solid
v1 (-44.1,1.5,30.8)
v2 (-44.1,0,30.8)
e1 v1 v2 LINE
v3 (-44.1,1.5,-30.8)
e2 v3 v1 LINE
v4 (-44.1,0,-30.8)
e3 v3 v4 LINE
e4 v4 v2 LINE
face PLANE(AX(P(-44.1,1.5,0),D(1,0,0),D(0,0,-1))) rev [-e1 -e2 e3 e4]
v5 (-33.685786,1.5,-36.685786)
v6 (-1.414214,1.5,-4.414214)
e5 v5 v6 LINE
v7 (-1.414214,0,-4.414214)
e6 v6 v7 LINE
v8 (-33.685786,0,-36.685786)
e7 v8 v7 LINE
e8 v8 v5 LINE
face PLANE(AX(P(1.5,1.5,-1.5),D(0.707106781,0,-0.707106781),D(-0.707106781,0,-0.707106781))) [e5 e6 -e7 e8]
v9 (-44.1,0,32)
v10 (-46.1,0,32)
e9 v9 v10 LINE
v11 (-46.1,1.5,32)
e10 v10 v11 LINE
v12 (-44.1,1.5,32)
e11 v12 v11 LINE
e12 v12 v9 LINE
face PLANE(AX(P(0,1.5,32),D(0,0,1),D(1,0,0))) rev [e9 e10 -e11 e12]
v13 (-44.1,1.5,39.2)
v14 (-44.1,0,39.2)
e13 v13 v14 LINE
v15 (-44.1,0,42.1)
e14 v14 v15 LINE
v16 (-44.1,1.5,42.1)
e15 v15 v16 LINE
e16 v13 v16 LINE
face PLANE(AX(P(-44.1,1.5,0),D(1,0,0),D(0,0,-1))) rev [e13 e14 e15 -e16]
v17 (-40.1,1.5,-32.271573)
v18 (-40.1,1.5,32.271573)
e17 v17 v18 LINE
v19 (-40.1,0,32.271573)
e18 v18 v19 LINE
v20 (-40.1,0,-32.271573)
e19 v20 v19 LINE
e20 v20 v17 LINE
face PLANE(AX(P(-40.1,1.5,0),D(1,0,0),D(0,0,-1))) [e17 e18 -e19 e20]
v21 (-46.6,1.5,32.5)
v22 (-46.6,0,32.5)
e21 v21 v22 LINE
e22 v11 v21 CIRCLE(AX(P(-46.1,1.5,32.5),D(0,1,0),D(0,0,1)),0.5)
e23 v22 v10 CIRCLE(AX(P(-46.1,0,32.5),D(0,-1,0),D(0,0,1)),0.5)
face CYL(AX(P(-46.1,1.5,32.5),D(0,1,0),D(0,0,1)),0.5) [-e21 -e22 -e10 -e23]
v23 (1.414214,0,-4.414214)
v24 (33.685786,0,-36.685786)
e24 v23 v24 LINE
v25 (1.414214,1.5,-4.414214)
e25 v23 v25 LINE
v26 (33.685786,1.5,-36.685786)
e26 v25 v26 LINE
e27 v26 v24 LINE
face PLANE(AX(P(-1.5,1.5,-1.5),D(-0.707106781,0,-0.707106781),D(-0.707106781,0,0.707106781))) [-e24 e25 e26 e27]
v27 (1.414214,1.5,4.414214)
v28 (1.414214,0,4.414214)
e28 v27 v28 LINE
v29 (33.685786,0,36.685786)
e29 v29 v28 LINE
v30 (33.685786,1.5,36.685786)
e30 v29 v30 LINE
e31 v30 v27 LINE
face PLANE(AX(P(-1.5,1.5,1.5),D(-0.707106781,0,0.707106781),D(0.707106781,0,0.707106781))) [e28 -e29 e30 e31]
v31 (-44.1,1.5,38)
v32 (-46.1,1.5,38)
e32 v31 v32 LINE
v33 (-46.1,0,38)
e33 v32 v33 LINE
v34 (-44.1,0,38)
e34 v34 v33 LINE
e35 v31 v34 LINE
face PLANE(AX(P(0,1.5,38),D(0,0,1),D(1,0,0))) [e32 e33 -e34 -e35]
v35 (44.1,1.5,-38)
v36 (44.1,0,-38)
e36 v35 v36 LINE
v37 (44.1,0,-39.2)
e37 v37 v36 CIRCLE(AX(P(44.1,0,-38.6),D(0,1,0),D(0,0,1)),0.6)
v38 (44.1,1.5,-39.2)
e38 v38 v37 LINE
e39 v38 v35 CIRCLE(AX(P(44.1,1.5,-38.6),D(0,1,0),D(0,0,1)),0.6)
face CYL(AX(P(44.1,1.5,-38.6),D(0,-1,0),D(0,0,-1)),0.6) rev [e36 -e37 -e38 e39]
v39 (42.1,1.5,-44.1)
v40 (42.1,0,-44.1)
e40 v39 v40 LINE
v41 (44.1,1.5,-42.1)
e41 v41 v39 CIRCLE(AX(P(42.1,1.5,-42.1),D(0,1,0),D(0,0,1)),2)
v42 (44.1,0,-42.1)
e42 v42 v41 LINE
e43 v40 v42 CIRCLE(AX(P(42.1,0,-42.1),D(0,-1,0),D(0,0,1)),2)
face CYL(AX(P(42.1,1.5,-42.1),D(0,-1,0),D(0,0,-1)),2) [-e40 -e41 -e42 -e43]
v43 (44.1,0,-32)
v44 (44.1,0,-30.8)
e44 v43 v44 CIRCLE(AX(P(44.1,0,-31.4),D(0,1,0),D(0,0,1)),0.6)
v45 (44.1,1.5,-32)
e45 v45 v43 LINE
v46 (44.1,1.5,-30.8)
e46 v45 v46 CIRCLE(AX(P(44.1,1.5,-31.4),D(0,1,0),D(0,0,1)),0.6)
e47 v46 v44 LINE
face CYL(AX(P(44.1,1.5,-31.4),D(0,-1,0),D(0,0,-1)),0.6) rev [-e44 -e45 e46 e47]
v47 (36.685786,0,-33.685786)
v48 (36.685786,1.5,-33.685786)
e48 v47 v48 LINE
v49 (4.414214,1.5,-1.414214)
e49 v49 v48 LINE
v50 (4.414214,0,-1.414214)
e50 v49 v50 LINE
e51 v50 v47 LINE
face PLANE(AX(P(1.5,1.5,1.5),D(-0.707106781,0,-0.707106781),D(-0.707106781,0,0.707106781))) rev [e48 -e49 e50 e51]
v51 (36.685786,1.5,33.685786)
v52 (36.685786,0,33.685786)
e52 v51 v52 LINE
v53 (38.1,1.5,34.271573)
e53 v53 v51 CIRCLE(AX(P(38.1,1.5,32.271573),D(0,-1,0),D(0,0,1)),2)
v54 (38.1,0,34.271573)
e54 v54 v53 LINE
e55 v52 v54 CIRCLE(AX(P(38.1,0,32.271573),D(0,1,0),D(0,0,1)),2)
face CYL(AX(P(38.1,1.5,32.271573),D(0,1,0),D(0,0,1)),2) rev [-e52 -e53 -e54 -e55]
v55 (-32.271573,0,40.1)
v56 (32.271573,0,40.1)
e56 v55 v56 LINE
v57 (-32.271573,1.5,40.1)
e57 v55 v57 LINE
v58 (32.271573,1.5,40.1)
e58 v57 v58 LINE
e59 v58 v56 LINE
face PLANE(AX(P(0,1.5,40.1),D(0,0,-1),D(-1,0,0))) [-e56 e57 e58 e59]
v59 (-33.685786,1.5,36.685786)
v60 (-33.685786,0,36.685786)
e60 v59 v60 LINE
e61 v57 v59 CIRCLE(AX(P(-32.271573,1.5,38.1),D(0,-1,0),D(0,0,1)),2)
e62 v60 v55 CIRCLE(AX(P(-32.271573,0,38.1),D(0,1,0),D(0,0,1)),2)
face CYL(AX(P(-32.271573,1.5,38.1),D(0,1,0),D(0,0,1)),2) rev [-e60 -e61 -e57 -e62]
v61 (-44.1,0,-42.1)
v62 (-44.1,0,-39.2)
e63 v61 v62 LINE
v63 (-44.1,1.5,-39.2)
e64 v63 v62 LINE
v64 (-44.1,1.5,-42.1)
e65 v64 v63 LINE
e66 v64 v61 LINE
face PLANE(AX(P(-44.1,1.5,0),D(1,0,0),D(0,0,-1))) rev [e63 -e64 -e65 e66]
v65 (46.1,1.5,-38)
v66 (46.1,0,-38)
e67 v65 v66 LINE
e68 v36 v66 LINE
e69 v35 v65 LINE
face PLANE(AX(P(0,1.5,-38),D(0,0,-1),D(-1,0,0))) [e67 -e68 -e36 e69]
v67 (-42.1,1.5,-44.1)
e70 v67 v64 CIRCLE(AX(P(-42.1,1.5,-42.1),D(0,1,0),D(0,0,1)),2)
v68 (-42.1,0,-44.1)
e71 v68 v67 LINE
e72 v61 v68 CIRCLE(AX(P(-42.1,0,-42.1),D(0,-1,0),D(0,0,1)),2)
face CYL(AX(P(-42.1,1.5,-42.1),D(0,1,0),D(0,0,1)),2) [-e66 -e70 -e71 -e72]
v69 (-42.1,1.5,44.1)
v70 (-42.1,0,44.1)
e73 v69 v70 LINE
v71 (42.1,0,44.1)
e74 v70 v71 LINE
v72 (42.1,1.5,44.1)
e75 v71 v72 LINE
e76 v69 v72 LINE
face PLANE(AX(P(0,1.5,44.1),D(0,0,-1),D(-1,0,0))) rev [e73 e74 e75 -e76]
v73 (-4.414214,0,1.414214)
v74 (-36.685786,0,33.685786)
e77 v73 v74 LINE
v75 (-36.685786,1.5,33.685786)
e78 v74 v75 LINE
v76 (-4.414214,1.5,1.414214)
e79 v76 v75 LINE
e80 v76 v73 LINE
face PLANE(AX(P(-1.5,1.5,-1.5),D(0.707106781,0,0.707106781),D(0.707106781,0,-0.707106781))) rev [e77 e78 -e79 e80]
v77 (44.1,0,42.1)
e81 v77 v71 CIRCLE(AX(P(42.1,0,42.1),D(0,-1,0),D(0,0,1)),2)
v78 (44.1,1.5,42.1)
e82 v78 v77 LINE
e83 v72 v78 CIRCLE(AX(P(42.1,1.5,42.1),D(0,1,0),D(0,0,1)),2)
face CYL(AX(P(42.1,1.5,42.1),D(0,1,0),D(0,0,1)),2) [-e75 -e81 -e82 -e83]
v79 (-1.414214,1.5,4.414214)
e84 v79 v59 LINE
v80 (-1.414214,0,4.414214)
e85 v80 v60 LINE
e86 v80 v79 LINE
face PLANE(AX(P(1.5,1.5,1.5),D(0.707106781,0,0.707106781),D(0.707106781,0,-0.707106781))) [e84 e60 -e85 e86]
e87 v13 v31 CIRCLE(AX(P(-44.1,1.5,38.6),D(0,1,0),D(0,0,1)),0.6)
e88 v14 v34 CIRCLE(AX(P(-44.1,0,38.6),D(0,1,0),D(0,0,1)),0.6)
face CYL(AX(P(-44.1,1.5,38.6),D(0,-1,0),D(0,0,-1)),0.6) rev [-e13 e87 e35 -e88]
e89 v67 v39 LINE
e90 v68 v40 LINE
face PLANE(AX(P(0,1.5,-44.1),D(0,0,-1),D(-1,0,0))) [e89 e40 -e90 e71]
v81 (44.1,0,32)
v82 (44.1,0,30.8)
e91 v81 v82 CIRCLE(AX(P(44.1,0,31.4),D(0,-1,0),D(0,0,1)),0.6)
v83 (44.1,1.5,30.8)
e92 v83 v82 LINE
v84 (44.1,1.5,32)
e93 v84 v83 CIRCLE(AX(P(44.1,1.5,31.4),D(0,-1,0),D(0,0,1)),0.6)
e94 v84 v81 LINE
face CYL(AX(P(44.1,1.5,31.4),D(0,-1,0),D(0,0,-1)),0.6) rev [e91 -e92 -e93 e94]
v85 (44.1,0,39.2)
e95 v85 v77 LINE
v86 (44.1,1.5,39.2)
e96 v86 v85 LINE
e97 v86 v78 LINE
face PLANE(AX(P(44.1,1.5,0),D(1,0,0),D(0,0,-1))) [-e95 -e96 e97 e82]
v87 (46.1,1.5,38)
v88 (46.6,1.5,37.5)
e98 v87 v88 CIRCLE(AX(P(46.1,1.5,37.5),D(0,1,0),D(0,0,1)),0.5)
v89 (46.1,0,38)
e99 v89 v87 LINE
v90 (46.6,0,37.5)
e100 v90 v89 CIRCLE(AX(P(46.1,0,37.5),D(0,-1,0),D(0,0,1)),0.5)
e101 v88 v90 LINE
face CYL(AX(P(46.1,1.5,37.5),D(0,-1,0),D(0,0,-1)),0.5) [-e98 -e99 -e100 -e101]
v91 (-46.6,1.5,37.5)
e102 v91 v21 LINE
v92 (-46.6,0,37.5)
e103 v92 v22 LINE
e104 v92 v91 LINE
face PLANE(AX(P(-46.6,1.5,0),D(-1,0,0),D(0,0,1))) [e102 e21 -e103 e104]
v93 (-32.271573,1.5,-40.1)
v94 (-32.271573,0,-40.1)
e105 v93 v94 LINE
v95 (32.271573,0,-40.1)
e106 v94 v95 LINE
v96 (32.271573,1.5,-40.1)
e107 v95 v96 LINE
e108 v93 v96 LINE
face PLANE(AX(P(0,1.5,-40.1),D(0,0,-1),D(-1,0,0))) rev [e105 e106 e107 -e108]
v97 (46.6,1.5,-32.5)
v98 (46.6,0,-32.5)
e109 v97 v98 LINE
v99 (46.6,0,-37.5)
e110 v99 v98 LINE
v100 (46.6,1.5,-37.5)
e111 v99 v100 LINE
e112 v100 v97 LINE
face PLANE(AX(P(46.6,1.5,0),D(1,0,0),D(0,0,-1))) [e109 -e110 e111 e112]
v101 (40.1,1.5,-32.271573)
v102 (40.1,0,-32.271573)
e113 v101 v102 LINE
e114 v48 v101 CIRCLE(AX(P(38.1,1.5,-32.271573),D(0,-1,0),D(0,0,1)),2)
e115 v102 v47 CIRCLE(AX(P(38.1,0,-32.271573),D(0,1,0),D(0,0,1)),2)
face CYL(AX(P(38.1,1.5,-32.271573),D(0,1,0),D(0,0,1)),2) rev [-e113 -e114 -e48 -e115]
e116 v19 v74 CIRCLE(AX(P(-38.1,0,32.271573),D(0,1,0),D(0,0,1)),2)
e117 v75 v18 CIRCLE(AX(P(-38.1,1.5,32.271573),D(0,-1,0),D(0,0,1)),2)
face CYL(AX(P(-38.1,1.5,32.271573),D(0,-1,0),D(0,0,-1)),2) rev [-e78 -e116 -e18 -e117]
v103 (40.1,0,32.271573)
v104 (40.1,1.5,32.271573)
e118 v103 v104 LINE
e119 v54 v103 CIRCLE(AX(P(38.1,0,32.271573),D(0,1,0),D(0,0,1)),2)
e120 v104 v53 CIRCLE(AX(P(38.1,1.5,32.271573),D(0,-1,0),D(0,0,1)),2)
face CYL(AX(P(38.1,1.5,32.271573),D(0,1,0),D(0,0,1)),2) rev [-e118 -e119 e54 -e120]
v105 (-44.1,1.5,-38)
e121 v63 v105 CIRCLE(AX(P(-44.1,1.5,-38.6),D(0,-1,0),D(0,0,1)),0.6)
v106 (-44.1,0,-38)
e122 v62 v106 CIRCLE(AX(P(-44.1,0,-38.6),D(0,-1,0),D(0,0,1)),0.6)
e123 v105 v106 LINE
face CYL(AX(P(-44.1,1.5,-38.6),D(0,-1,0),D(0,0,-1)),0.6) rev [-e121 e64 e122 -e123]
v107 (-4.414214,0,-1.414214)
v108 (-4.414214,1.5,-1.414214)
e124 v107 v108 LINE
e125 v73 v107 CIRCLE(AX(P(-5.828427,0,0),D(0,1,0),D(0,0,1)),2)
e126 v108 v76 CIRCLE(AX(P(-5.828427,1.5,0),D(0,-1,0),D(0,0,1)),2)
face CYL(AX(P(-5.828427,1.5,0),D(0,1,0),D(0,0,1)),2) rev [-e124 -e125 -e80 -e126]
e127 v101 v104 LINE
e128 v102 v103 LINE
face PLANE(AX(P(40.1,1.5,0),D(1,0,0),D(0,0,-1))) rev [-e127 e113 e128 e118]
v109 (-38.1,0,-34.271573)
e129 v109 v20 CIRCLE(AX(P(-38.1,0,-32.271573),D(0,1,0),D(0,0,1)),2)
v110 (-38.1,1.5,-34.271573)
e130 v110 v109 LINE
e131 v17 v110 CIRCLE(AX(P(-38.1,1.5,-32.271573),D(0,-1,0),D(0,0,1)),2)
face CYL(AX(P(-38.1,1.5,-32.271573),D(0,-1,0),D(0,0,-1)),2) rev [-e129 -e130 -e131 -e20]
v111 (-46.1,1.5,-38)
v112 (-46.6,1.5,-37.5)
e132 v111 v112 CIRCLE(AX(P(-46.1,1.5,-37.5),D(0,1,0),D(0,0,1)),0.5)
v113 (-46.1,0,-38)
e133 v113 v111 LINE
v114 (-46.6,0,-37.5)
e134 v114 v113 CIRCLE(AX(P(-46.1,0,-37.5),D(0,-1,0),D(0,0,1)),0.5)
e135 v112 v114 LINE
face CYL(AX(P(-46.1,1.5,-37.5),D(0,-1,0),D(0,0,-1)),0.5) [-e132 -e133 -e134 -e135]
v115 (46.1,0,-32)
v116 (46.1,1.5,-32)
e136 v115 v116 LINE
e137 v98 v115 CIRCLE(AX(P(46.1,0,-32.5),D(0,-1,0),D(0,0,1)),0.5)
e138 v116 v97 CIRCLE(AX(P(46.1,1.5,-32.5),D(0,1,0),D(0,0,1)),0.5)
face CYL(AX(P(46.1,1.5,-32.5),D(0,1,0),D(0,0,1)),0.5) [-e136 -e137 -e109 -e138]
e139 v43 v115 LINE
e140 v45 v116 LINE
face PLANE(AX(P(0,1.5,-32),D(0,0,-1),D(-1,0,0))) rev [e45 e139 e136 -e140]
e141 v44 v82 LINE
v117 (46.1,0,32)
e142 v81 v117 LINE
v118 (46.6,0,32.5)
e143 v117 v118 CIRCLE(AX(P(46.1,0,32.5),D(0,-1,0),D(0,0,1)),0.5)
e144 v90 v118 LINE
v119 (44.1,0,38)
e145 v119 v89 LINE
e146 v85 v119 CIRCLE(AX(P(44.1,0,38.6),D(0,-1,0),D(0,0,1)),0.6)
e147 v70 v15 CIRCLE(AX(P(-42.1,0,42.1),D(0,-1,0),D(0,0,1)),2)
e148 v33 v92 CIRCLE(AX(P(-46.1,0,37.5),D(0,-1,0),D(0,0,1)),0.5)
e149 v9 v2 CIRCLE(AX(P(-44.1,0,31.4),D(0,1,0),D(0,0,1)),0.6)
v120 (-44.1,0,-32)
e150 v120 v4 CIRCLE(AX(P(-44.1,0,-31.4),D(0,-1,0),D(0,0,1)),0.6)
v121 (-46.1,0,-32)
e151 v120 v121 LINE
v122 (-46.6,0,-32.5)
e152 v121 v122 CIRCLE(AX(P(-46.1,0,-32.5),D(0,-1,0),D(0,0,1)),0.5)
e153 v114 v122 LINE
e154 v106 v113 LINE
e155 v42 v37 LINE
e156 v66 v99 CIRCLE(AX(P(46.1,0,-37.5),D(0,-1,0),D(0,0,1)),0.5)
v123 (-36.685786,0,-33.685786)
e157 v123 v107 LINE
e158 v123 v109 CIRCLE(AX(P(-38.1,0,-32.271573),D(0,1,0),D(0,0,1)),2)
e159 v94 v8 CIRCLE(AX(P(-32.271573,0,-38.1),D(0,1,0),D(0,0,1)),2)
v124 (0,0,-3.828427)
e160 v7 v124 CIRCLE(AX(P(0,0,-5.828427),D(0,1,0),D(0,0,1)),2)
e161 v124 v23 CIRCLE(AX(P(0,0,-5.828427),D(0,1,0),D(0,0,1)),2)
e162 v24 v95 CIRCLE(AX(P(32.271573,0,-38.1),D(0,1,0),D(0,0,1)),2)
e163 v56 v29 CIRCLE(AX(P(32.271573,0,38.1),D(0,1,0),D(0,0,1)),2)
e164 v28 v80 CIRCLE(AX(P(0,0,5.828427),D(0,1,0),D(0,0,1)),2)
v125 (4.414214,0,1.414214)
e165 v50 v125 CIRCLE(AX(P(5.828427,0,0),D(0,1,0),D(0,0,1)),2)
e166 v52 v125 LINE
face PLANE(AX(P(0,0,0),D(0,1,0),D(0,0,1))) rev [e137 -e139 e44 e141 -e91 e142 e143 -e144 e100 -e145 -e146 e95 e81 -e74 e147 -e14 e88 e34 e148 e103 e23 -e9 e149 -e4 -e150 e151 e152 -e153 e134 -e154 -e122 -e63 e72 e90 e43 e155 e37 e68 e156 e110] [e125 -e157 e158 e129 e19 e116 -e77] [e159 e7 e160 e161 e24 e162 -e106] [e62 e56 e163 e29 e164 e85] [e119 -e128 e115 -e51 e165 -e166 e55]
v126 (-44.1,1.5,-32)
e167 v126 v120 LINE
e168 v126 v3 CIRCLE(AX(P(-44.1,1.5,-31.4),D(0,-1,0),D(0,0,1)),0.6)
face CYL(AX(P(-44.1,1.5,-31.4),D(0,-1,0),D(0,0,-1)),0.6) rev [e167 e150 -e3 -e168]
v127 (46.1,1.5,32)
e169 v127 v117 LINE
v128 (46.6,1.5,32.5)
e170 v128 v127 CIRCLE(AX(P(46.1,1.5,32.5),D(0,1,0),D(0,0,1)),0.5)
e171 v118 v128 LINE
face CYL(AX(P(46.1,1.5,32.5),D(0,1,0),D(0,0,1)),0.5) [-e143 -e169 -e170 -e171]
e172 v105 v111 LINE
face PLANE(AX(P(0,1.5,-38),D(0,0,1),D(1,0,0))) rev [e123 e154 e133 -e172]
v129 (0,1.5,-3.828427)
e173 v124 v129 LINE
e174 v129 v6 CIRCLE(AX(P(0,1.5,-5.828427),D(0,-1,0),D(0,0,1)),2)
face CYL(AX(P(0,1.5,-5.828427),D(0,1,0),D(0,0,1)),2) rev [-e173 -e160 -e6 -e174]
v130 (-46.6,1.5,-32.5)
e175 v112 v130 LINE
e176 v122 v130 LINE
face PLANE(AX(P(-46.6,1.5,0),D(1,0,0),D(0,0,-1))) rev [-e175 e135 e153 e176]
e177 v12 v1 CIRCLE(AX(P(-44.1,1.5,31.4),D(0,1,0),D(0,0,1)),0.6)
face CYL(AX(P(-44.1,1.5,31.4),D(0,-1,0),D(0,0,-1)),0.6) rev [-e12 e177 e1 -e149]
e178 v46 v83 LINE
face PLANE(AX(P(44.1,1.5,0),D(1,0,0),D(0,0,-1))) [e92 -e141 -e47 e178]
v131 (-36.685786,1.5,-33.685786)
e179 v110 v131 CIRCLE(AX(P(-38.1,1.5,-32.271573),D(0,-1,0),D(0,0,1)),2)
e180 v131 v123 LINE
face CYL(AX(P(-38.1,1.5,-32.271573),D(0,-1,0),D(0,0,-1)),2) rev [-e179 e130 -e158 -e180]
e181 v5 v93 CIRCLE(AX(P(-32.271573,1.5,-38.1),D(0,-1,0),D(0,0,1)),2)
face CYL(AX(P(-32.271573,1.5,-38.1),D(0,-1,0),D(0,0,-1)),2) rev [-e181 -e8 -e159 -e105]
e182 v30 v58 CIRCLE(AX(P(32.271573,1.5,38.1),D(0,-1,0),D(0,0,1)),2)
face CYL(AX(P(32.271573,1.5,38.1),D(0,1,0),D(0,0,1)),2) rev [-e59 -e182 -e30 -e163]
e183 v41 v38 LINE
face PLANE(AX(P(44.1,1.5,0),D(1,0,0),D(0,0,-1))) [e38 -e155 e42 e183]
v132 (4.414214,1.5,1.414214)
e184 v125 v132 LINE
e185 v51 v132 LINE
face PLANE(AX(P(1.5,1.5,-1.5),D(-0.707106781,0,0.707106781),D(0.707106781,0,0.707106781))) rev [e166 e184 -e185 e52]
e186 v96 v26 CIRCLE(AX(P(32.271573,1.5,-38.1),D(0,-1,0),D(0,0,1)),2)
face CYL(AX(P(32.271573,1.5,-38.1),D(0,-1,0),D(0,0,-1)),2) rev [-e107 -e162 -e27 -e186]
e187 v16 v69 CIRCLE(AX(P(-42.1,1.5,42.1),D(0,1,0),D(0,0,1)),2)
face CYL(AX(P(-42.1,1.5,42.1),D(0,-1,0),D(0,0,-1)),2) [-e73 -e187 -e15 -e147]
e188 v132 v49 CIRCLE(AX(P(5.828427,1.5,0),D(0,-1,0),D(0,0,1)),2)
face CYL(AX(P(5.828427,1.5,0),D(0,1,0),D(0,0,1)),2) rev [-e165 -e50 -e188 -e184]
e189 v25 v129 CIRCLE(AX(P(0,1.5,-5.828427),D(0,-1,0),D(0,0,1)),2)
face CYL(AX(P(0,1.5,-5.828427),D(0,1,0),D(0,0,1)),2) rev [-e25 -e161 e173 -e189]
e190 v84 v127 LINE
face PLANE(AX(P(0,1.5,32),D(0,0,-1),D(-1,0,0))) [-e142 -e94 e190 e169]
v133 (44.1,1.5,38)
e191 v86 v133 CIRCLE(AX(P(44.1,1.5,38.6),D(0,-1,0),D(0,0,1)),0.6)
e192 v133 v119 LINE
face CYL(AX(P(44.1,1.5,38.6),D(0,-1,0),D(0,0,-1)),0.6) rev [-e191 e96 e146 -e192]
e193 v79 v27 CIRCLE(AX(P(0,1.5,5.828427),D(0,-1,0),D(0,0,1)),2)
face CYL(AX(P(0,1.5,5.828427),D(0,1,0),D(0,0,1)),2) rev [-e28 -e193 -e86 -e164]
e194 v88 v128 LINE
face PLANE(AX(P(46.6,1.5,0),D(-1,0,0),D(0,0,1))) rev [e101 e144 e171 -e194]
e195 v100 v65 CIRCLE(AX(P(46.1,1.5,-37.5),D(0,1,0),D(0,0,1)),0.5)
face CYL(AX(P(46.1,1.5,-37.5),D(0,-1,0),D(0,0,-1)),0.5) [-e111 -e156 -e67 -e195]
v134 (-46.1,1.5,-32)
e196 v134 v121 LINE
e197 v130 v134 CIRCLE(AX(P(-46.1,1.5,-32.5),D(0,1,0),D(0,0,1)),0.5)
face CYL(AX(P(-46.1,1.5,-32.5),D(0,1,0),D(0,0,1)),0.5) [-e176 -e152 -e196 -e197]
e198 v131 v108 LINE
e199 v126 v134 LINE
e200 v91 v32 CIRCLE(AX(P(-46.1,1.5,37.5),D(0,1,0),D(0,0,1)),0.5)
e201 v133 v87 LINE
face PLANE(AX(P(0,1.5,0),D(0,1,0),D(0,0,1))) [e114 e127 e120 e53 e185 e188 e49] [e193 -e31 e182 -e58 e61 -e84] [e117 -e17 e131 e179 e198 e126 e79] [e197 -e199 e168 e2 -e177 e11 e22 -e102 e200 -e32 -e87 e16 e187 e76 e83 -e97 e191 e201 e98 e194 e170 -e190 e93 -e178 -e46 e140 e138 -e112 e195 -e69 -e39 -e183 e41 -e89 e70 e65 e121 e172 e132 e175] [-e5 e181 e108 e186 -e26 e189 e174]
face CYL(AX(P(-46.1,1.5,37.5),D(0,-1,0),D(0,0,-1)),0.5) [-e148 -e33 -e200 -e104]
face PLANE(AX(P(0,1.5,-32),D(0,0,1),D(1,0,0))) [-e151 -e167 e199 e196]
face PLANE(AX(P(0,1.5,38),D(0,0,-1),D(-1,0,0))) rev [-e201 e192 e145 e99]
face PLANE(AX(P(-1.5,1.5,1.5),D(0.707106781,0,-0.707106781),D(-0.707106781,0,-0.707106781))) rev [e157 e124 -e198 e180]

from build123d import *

# Parameters (mm, degrees)
EXTRUDE_1_DEPTH = 1.5
FILLET_1_R      = 0.5
FILLET_2_R      = 2


with BuildPart() as part:
    # 草图1 → 凸台-拉伸1 (new body)
    with BuildSketch(Plane(origin=(0, 0, 0), x_dir=(1, 0, 0), z_dir=(0, 1, 0))):
        with BuildLine():
            Line((44.1, 44.1), (-44.1, 44.1))
            Line((-44.1, 44.1), (-44.1, 39.2))
            ThreePointArc((-44.1, 39.2), (-43.5, 38.6), (-44.1, 38))
            Line((-44.1, 38), (-46.6, 38))
            Line((-46.6, 38), (-46.6, 32))
            Line((-46.6, 32), (-44.1, 32))
            ThreePointArc((-44.1, 32), (-43.5, 31.4), (-44.1, 30.8))
            Line((-44.1, 30.8), (-44.1, -30.8))
            ThreePointArc((-44.1, -30.8), (-43.5, -31.4), (-44.1, -32))
            Line((-44.1, -32), (-46.6, -32))
            Line((-46.6, -32), (-46.6, -38))
            Line((-46.6, -38), (-44.1, -38))
            ThreePointArc((-44.1, -38), (-43.5, -38.6), (-44.1, -39.2))
            Line((-44.1, -39.2), (-44.1, -44.1))
            Line((-44.1, -44.1), (44.1, -44.1))
            Line((44.1, -44.1), (44.1, -39.2))
            ThreePointArc((44.1, -39.2), (43.5, -38.6), (44.1, -38))
            Line((44.1, -38), (46.6, -38))
            Line((46.6, -38), (46.6, -32))
            Line((46.6, -32), (44.1, -32))
            ThreePointArc((44.1, -32), (43.5, -31.4), (44.1, -30.8))
            Line((44.1, -30.8), (44.1, 30.8))
            ThreePointArc((44.1, 30.8), (43.5, 31.4), (44.1, 32))
            Line((44.1, 32), (46.6, 32))
            Line((46.6, 32), (46.6, 38))
            Line((46.6, 38), (44.1, 38))
            ThreePointArc((44.1, 38), (43.5, 38.6), (44.1, 39.2))
            Line((44.1, 39.2), (44.1, 44.1))
        make_face()
        Polygon((-37.1, 40.1), (37.1, 40.1), (0, 3), align=None, mode=Mode.SUBTRACT)
        Polygon((40.1, 37.1), (40.1, -37.1), (3, 0), align=None, mode=Mode.SUBTRACT)
        Polygon((37.1, -40.1), (-37.1, -40.1), (0, -3), align=None, mode=Mode.SUBTRACT)
        Polygon((-40.1, -37.1), (-40.1, 37.1), (-3, 0), align=None, mode=Mode.SUBTRACT)
    extrude(amount=EXTRUDE_1_DEPTH)

    # 圆角1
    fillet_1_edges = [part.edges().sort_by_distance(p)[0] for p in [
        (46.6, 0.75, -38),
        (46.6, 0.75, -32),
        (46.6, 0.75, 32),
        (46.6, 0.75, 38),
        (-46.6, 0.75, 38),
        (-46.6, 0.75, 32),
        (-46.6, 0.75, -32),
        (-46.6, 0.75, -38),
    ]]
    fillet(fillet_1_edges, radius=FILLET_1_R)

    # 圆角2
    fillet_2_edges = [part.edges().sort_by_distance(p)[0] for p in [
        (-44.1, 0.75, -44.1),
        (44.1, 0.75, -44.1),
        (44.1, 0.75, 44.1),
        (-44.1, 0.75, 44.1),
        (-40.1, 0.75, 37.1),
        (-3, 0.75, 0),
        (-40.1, 0.75, -37.1),
        (37.1, 0.75, 40.1),
        (0, 0.75, 3),
        (-37.1, 0.75, 40.1),
        (3, 0.75, 0),
        (40.1, 0.75, 37.1),
        (40.1, 0.75, -37.1),
        (0, 0.75, -3),
        (37.1, 0.75, -40.1),
        (-37.1, 0.75, -40.1),
    ]]
    fillet(fillet_2_edges, radius=FILLET_2_R)


solid = part.part
